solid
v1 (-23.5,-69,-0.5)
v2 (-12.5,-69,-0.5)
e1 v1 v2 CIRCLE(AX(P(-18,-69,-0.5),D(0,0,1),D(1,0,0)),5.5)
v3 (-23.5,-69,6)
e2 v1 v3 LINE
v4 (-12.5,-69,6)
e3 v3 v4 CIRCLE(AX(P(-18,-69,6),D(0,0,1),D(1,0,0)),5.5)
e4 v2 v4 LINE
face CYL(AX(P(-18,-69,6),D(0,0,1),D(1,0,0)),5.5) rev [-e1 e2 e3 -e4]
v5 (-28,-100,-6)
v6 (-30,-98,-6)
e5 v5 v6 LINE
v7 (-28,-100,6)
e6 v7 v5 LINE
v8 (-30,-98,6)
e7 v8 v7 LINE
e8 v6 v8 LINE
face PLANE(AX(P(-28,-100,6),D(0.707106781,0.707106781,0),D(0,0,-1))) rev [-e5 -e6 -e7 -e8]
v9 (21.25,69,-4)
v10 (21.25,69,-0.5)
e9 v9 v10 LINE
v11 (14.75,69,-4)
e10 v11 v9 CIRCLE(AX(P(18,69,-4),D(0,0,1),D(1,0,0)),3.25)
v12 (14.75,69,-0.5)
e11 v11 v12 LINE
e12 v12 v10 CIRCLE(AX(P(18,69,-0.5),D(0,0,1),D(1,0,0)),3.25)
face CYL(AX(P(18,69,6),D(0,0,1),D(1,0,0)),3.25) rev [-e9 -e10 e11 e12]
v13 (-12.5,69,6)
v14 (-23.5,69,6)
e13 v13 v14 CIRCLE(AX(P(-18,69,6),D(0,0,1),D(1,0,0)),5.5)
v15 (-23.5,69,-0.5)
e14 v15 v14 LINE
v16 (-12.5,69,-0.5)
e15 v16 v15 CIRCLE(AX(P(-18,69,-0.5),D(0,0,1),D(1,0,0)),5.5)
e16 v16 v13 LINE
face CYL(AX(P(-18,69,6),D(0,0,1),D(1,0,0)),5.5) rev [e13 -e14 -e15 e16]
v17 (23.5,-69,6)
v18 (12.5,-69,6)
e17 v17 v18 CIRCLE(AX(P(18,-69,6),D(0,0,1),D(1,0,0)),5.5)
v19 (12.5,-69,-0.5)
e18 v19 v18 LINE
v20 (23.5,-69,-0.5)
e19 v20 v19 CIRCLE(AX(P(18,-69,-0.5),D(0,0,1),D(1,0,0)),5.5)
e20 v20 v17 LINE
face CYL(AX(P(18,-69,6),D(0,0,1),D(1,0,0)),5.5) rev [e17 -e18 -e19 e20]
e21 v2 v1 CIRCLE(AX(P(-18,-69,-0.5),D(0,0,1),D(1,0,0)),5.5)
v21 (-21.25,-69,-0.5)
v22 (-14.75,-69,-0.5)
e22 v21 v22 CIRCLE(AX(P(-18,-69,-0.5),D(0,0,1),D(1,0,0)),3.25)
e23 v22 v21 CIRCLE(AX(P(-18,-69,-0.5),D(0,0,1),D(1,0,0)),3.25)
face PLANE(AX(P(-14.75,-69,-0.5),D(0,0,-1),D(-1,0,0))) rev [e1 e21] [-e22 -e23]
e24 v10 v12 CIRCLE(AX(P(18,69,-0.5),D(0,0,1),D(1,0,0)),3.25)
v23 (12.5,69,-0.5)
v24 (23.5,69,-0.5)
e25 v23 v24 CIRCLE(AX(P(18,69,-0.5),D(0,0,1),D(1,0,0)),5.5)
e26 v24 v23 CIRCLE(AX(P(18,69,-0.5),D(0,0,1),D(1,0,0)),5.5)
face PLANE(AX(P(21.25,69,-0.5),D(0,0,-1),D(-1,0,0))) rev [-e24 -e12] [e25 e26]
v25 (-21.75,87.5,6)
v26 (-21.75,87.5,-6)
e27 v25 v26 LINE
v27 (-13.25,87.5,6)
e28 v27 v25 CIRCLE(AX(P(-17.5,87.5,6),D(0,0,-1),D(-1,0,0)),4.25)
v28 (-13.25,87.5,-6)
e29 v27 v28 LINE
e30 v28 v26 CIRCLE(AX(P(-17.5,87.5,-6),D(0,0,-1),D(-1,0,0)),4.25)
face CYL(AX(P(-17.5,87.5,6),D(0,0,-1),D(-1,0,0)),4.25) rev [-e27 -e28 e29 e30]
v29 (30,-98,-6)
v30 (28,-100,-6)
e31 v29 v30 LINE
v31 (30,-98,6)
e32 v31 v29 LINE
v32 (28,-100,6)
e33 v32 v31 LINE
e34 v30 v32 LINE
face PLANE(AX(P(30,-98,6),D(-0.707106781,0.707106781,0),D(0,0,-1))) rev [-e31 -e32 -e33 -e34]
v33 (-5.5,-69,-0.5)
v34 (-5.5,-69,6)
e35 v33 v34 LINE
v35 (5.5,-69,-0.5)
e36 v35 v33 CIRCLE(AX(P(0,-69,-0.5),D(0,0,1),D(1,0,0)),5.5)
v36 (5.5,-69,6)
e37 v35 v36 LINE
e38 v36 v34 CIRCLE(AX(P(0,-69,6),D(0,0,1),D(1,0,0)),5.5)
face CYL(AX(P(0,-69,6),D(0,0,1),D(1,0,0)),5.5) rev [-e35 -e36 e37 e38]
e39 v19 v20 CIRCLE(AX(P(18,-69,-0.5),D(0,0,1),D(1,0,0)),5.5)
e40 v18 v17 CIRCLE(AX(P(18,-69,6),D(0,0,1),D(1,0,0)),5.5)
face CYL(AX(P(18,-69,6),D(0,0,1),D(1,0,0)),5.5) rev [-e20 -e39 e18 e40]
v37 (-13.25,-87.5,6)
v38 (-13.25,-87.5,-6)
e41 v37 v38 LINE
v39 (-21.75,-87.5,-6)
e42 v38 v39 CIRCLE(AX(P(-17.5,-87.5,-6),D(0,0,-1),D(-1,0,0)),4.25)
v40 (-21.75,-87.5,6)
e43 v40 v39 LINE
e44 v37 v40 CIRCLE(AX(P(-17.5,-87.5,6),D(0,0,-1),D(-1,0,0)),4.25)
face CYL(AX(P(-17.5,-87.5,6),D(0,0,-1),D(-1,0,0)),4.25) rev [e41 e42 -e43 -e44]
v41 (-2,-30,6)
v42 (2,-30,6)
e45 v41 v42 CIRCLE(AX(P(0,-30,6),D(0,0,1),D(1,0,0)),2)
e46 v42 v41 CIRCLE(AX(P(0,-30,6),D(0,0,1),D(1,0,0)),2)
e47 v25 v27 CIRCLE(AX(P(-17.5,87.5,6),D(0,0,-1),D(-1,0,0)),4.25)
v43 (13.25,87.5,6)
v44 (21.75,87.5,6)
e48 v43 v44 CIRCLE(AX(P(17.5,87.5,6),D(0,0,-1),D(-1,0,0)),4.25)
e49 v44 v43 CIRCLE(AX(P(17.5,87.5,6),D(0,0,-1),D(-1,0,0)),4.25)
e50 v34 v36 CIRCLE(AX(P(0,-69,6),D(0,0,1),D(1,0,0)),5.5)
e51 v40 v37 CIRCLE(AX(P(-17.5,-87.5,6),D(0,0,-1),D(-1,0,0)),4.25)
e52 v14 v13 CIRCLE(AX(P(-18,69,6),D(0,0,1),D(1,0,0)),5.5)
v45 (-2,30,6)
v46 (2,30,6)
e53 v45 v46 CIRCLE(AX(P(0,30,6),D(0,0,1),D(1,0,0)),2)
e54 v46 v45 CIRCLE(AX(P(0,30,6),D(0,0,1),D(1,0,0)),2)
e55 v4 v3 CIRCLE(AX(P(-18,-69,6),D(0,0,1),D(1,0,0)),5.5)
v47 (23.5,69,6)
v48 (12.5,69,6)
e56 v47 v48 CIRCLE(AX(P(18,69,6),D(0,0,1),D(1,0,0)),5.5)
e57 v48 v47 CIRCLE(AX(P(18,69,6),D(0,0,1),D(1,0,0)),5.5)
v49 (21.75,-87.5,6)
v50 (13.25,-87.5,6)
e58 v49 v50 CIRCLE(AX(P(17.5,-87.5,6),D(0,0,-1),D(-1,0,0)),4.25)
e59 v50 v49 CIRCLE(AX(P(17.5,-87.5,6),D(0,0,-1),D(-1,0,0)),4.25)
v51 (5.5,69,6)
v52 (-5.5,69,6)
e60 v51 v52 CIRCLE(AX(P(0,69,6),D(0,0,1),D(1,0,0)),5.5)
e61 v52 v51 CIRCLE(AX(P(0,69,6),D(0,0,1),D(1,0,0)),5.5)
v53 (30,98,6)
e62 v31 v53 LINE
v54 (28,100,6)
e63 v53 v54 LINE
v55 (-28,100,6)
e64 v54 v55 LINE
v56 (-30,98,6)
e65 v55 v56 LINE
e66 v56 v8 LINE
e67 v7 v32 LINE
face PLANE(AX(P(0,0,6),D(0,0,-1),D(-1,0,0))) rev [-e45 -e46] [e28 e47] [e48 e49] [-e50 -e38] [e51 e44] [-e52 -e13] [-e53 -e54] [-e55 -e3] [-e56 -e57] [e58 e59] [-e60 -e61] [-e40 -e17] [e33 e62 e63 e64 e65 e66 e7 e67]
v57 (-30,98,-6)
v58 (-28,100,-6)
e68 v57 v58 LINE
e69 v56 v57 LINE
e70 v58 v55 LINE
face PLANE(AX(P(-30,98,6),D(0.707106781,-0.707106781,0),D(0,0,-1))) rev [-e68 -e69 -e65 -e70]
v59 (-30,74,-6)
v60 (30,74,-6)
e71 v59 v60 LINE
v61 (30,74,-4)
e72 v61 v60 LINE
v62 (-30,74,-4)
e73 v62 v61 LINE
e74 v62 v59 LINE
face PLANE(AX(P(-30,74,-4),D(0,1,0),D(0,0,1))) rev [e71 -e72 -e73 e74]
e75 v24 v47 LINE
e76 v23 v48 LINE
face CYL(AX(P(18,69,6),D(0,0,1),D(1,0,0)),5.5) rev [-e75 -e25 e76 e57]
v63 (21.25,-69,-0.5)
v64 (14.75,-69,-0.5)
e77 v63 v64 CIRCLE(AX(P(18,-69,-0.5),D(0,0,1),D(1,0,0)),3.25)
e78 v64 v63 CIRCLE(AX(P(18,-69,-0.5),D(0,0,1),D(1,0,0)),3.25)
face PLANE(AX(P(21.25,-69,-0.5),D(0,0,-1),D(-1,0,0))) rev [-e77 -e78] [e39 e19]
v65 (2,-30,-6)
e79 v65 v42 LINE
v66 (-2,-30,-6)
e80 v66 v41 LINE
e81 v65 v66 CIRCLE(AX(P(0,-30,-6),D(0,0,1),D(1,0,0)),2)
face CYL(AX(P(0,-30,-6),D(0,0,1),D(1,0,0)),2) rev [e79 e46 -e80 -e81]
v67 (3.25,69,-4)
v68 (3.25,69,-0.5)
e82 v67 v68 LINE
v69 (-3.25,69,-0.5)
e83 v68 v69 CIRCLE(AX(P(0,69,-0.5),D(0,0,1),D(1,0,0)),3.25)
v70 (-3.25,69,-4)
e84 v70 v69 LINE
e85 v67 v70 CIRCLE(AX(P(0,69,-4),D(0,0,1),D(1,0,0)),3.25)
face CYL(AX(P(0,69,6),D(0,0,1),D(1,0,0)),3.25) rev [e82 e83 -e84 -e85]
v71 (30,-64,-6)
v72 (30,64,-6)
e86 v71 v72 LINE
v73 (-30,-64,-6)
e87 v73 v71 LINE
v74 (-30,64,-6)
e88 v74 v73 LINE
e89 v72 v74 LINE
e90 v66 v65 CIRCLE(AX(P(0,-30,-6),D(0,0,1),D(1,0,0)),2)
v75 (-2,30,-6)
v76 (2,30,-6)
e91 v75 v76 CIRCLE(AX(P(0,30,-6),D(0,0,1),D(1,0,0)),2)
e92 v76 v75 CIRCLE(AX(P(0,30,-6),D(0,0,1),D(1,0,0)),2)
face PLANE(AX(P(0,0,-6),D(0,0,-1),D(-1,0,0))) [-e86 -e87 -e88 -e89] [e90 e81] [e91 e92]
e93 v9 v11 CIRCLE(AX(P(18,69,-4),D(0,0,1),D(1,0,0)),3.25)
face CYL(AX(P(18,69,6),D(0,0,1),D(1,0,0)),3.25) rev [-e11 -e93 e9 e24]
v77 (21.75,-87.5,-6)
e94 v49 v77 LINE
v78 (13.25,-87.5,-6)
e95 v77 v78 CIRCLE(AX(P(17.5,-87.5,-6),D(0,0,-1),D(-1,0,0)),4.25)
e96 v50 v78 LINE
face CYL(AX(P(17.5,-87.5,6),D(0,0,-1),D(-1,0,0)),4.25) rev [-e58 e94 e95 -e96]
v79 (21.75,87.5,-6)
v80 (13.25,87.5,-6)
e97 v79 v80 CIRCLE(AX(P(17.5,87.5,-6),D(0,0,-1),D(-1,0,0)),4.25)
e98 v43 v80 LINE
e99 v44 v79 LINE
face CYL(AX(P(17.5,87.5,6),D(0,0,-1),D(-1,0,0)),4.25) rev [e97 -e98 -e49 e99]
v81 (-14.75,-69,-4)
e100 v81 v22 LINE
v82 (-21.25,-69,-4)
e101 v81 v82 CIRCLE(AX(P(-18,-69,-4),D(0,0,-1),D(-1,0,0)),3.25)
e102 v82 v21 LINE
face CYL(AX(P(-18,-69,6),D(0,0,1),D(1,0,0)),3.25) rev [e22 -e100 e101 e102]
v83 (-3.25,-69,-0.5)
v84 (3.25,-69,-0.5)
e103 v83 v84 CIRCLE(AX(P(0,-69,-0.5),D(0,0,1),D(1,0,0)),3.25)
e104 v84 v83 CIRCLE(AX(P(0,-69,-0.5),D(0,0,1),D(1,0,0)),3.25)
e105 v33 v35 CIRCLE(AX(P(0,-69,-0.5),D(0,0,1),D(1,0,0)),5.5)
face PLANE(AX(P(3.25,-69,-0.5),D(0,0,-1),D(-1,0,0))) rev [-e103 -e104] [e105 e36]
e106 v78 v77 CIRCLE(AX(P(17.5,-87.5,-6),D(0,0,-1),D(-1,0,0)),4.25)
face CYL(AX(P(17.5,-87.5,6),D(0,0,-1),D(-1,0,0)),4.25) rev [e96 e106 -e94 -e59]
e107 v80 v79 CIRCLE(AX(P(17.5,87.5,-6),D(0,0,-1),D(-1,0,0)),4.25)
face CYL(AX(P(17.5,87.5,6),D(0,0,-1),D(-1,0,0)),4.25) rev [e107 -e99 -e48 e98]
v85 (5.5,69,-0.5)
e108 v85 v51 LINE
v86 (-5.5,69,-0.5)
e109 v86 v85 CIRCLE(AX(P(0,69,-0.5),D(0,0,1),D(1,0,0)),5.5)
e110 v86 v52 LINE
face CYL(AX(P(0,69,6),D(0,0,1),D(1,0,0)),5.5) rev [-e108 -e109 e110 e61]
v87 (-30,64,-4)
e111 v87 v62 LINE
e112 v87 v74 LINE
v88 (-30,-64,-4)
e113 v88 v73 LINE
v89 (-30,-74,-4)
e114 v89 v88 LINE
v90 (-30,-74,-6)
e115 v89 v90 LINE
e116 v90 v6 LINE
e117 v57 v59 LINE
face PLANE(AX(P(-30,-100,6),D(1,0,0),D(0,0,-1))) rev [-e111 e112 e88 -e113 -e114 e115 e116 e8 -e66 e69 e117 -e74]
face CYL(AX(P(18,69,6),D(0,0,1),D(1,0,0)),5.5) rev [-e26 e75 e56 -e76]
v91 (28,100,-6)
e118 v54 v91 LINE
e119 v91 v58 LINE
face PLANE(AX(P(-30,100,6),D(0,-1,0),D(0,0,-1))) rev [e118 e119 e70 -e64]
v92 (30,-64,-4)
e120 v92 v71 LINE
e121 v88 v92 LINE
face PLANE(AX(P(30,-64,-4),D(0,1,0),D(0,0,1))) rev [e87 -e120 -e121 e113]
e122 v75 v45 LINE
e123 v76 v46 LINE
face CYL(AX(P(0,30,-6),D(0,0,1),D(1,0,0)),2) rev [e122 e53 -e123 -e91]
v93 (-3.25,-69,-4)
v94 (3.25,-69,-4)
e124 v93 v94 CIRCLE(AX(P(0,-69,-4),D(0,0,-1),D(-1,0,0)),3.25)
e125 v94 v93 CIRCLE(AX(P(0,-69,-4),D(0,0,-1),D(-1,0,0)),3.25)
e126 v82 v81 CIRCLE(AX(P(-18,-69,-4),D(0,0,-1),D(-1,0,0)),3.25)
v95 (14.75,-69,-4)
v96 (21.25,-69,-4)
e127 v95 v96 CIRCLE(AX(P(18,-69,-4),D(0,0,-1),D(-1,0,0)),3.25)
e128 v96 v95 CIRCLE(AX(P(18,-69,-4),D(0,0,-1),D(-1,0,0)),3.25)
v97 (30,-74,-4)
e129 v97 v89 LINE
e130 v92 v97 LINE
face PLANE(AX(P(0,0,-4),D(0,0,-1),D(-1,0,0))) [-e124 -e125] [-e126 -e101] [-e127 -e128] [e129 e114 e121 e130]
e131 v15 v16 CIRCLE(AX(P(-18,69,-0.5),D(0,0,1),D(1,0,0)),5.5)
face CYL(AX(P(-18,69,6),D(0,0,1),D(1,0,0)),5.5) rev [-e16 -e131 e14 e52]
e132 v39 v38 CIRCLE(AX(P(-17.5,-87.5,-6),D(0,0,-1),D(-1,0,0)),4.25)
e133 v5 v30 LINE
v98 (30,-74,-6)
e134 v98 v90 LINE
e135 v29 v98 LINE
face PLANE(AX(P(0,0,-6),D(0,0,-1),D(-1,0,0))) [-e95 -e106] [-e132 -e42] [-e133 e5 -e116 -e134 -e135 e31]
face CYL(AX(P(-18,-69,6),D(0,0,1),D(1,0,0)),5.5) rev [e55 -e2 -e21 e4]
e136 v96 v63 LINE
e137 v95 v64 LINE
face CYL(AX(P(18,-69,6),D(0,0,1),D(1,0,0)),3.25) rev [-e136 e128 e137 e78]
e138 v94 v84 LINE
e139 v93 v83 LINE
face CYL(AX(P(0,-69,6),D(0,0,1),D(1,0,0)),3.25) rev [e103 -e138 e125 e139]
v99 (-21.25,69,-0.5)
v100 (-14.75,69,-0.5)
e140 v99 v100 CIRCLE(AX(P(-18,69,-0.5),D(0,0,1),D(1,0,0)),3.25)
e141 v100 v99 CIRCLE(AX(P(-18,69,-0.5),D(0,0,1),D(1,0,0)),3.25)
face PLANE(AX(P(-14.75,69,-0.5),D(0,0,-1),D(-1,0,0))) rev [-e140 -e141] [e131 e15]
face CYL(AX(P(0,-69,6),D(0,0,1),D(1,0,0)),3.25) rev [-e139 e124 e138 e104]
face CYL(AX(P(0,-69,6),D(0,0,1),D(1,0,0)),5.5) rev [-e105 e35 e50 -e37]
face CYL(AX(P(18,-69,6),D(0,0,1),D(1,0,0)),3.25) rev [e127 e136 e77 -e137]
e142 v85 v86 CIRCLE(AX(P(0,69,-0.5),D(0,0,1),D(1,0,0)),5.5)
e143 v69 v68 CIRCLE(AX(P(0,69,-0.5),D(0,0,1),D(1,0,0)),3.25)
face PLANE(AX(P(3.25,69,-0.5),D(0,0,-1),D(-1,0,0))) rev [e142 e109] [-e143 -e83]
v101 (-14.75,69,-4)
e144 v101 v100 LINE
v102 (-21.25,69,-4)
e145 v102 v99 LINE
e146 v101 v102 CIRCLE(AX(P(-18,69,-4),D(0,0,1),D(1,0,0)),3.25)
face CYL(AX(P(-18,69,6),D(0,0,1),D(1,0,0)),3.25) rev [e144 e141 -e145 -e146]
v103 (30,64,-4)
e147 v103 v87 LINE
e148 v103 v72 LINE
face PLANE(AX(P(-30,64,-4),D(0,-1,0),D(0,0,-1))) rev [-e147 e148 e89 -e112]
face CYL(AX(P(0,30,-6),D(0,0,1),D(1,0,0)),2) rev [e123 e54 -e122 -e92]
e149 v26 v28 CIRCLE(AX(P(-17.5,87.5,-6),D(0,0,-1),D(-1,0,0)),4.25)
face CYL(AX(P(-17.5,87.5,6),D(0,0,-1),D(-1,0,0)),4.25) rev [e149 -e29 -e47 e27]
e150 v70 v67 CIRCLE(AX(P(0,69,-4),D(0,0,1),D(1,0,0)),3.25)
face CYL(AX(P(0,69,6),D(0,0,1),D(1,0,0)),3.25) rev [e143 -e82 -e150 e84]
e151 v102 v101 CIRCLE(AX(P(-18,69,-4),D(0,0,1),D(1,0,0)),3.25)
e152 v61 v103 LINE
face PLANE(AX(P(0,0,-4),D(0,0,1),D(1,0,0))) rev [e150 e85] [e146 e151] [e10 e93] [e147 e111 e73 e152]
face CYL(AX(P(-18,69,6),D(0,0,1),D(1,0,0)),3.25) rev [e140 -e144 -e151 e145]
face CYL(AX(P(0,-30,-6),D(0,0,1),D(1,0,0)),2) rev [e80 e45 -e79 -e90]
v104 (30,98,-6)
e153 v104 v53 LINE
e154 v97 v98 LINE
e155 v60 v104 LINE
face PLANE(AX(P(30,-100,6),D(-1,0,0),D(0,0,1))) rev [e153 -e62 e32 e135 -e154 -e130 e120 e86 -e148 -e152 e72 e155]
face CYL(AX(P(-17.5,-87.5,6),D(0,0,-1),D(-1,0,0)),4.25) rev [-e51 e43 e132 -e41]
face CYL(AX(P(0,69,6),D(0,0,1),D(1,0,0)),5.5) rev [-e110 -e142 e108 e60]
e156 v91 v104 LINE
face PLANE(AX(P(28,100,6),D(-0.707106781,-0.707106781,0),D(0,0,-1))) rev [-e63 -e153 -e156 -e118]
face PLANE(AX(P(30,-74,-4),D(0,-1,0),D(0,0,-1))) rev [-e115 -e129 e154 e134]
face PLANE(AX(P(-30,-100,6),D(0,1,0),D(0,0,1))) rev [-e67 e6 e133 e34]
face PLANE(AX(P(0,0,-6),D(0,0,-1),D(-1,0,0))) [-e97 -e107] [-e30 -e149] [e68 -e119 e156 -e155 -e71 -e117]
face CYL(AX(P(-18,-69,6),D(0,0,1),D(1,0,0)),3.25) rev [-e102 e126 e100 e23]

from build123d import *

# Parameters (mm, degrees)
SKETCH1_W                                            = 60
SKETCH1_H                                            = 200
BOSS_EXTRUDE1_DEPTH                                  = 6
CHAMFER1_SIZE                                        = 2
SKETCH2_W                                            = 60
SKETCH2_H                                            = 10
CUT_EXTRUDE1_DEPTH                                   = 2
HOLE_SIZE_PER_SOCKET_HEAD_CAP_SCREW_TYPE_D           = 6.5
HOLE_SIZE_PER_SOCKET_HEAD_CAP_SCREW_TYPE_CBORE_D     = 11
HOLE_SIZE_PER_SOCKET_HEAD_CAP_SCREW_TYPE_CBORE_DEPTH = 6.5
SKETCH5_R                                            = 4.25
CUT_EXTRUDE2_DEPTH                                   = 106.090437243
SKETCH6_R                                            = 2
CUT_EXTRUDE3_DEPTH                                   = 106.090437243


with BuildPart() as part:
    # Sketch1 → Boss-Extrude1 (new, symmetric)
    with BuildSketch(Plane.XY):
        Rectangle(SKETCH1_W, SKETCH1_H)
    extrude(amount=BOSS_EXTRUDE1_DEPTH, both=True)

    # Chamfer1
    chamfer1_edges = [part.edges().sort_by_distance(p)[0] for p in [
        (30, -100, 0),
        (-30, -100, 0),
        (-30, 100, 0),
        (30, 100, 0),
    ]]
    chamfer(chamfer1_edges, length=CHAMFER1_SIZE)

    # Sketch2 → Cut-Extrude1 (cut)
    with BuildSketch(Plane(origin=(0, 0, -6), x_dir=(-1, 0, 0), z_dir=(0, 0, -1))):
        with Locations((0, 69)):
            Rectangle(SKETCH2_W, SKETCH2_H)
        with Locations((0, -69)):
            Rectangle(SKETCH2_W, SKETCH2_H)
    extrude(amount=-CUT_EXTRUDE1_DEPTH, mode=Mode.SUBTRACT)

    # Hole size per socket head cap screw type 1 (through all)
    with Locations(Plane.XY.offset(6)):
        with Locations((-18, -69), (0, -69), (18, -69), (18, 69), (0, 69), (-18, 69)):
            CounterBoreHole(HOLE_SIZE_PER_SOCKET_HEAD_CAP_SCREW_TYPE_D / 2, HOLE_SIZE_PER_SOCKET_HEAD_CAP_SCREW_TYPE_CBORE_D / 2, HOLE_SIZE_PER_SOCKET_HEAD_CAP_SCREW_TYPE_CBORE_DEPTH)

    # Sketch5 → Cut-Extrude2 (cut, through all)
    with BuildSketch(Plane(origin=(0, 0, -6), x_dir=(-1, 0, 0), z_dir=(0, 0, -1))):
        with Locations((17.5, 87.5)):
            Circle(SKETCH5_R)
        with Locations((-17.5, 87.5)):
            Circle(SKETCH5_R)
        with Locations((17.5, -87.5)):
            Circle(SKETCH5_R)
        with Locations((-17.5, -87.5)):
            Circle(SKETCH5_R)
    extrude(amount=-CUT_EXTRUDE2_DEPTH, mode=Mode.SUBTRACT)

    # Sketch6 → Cut-Extrude3 (cut, through all)
    with BuildSketch(Plane.XY.offset(6)):
        with Locations((0, 30)):
            Circle(SKETCH6_R)
        with Locations((0, -30)):
            Circle(SKETCH6_R)
    extrude(amount=-CUT_EXTRUDE3_DEPTH, mode=Mode.SUBTRACT)


solid = part.part
